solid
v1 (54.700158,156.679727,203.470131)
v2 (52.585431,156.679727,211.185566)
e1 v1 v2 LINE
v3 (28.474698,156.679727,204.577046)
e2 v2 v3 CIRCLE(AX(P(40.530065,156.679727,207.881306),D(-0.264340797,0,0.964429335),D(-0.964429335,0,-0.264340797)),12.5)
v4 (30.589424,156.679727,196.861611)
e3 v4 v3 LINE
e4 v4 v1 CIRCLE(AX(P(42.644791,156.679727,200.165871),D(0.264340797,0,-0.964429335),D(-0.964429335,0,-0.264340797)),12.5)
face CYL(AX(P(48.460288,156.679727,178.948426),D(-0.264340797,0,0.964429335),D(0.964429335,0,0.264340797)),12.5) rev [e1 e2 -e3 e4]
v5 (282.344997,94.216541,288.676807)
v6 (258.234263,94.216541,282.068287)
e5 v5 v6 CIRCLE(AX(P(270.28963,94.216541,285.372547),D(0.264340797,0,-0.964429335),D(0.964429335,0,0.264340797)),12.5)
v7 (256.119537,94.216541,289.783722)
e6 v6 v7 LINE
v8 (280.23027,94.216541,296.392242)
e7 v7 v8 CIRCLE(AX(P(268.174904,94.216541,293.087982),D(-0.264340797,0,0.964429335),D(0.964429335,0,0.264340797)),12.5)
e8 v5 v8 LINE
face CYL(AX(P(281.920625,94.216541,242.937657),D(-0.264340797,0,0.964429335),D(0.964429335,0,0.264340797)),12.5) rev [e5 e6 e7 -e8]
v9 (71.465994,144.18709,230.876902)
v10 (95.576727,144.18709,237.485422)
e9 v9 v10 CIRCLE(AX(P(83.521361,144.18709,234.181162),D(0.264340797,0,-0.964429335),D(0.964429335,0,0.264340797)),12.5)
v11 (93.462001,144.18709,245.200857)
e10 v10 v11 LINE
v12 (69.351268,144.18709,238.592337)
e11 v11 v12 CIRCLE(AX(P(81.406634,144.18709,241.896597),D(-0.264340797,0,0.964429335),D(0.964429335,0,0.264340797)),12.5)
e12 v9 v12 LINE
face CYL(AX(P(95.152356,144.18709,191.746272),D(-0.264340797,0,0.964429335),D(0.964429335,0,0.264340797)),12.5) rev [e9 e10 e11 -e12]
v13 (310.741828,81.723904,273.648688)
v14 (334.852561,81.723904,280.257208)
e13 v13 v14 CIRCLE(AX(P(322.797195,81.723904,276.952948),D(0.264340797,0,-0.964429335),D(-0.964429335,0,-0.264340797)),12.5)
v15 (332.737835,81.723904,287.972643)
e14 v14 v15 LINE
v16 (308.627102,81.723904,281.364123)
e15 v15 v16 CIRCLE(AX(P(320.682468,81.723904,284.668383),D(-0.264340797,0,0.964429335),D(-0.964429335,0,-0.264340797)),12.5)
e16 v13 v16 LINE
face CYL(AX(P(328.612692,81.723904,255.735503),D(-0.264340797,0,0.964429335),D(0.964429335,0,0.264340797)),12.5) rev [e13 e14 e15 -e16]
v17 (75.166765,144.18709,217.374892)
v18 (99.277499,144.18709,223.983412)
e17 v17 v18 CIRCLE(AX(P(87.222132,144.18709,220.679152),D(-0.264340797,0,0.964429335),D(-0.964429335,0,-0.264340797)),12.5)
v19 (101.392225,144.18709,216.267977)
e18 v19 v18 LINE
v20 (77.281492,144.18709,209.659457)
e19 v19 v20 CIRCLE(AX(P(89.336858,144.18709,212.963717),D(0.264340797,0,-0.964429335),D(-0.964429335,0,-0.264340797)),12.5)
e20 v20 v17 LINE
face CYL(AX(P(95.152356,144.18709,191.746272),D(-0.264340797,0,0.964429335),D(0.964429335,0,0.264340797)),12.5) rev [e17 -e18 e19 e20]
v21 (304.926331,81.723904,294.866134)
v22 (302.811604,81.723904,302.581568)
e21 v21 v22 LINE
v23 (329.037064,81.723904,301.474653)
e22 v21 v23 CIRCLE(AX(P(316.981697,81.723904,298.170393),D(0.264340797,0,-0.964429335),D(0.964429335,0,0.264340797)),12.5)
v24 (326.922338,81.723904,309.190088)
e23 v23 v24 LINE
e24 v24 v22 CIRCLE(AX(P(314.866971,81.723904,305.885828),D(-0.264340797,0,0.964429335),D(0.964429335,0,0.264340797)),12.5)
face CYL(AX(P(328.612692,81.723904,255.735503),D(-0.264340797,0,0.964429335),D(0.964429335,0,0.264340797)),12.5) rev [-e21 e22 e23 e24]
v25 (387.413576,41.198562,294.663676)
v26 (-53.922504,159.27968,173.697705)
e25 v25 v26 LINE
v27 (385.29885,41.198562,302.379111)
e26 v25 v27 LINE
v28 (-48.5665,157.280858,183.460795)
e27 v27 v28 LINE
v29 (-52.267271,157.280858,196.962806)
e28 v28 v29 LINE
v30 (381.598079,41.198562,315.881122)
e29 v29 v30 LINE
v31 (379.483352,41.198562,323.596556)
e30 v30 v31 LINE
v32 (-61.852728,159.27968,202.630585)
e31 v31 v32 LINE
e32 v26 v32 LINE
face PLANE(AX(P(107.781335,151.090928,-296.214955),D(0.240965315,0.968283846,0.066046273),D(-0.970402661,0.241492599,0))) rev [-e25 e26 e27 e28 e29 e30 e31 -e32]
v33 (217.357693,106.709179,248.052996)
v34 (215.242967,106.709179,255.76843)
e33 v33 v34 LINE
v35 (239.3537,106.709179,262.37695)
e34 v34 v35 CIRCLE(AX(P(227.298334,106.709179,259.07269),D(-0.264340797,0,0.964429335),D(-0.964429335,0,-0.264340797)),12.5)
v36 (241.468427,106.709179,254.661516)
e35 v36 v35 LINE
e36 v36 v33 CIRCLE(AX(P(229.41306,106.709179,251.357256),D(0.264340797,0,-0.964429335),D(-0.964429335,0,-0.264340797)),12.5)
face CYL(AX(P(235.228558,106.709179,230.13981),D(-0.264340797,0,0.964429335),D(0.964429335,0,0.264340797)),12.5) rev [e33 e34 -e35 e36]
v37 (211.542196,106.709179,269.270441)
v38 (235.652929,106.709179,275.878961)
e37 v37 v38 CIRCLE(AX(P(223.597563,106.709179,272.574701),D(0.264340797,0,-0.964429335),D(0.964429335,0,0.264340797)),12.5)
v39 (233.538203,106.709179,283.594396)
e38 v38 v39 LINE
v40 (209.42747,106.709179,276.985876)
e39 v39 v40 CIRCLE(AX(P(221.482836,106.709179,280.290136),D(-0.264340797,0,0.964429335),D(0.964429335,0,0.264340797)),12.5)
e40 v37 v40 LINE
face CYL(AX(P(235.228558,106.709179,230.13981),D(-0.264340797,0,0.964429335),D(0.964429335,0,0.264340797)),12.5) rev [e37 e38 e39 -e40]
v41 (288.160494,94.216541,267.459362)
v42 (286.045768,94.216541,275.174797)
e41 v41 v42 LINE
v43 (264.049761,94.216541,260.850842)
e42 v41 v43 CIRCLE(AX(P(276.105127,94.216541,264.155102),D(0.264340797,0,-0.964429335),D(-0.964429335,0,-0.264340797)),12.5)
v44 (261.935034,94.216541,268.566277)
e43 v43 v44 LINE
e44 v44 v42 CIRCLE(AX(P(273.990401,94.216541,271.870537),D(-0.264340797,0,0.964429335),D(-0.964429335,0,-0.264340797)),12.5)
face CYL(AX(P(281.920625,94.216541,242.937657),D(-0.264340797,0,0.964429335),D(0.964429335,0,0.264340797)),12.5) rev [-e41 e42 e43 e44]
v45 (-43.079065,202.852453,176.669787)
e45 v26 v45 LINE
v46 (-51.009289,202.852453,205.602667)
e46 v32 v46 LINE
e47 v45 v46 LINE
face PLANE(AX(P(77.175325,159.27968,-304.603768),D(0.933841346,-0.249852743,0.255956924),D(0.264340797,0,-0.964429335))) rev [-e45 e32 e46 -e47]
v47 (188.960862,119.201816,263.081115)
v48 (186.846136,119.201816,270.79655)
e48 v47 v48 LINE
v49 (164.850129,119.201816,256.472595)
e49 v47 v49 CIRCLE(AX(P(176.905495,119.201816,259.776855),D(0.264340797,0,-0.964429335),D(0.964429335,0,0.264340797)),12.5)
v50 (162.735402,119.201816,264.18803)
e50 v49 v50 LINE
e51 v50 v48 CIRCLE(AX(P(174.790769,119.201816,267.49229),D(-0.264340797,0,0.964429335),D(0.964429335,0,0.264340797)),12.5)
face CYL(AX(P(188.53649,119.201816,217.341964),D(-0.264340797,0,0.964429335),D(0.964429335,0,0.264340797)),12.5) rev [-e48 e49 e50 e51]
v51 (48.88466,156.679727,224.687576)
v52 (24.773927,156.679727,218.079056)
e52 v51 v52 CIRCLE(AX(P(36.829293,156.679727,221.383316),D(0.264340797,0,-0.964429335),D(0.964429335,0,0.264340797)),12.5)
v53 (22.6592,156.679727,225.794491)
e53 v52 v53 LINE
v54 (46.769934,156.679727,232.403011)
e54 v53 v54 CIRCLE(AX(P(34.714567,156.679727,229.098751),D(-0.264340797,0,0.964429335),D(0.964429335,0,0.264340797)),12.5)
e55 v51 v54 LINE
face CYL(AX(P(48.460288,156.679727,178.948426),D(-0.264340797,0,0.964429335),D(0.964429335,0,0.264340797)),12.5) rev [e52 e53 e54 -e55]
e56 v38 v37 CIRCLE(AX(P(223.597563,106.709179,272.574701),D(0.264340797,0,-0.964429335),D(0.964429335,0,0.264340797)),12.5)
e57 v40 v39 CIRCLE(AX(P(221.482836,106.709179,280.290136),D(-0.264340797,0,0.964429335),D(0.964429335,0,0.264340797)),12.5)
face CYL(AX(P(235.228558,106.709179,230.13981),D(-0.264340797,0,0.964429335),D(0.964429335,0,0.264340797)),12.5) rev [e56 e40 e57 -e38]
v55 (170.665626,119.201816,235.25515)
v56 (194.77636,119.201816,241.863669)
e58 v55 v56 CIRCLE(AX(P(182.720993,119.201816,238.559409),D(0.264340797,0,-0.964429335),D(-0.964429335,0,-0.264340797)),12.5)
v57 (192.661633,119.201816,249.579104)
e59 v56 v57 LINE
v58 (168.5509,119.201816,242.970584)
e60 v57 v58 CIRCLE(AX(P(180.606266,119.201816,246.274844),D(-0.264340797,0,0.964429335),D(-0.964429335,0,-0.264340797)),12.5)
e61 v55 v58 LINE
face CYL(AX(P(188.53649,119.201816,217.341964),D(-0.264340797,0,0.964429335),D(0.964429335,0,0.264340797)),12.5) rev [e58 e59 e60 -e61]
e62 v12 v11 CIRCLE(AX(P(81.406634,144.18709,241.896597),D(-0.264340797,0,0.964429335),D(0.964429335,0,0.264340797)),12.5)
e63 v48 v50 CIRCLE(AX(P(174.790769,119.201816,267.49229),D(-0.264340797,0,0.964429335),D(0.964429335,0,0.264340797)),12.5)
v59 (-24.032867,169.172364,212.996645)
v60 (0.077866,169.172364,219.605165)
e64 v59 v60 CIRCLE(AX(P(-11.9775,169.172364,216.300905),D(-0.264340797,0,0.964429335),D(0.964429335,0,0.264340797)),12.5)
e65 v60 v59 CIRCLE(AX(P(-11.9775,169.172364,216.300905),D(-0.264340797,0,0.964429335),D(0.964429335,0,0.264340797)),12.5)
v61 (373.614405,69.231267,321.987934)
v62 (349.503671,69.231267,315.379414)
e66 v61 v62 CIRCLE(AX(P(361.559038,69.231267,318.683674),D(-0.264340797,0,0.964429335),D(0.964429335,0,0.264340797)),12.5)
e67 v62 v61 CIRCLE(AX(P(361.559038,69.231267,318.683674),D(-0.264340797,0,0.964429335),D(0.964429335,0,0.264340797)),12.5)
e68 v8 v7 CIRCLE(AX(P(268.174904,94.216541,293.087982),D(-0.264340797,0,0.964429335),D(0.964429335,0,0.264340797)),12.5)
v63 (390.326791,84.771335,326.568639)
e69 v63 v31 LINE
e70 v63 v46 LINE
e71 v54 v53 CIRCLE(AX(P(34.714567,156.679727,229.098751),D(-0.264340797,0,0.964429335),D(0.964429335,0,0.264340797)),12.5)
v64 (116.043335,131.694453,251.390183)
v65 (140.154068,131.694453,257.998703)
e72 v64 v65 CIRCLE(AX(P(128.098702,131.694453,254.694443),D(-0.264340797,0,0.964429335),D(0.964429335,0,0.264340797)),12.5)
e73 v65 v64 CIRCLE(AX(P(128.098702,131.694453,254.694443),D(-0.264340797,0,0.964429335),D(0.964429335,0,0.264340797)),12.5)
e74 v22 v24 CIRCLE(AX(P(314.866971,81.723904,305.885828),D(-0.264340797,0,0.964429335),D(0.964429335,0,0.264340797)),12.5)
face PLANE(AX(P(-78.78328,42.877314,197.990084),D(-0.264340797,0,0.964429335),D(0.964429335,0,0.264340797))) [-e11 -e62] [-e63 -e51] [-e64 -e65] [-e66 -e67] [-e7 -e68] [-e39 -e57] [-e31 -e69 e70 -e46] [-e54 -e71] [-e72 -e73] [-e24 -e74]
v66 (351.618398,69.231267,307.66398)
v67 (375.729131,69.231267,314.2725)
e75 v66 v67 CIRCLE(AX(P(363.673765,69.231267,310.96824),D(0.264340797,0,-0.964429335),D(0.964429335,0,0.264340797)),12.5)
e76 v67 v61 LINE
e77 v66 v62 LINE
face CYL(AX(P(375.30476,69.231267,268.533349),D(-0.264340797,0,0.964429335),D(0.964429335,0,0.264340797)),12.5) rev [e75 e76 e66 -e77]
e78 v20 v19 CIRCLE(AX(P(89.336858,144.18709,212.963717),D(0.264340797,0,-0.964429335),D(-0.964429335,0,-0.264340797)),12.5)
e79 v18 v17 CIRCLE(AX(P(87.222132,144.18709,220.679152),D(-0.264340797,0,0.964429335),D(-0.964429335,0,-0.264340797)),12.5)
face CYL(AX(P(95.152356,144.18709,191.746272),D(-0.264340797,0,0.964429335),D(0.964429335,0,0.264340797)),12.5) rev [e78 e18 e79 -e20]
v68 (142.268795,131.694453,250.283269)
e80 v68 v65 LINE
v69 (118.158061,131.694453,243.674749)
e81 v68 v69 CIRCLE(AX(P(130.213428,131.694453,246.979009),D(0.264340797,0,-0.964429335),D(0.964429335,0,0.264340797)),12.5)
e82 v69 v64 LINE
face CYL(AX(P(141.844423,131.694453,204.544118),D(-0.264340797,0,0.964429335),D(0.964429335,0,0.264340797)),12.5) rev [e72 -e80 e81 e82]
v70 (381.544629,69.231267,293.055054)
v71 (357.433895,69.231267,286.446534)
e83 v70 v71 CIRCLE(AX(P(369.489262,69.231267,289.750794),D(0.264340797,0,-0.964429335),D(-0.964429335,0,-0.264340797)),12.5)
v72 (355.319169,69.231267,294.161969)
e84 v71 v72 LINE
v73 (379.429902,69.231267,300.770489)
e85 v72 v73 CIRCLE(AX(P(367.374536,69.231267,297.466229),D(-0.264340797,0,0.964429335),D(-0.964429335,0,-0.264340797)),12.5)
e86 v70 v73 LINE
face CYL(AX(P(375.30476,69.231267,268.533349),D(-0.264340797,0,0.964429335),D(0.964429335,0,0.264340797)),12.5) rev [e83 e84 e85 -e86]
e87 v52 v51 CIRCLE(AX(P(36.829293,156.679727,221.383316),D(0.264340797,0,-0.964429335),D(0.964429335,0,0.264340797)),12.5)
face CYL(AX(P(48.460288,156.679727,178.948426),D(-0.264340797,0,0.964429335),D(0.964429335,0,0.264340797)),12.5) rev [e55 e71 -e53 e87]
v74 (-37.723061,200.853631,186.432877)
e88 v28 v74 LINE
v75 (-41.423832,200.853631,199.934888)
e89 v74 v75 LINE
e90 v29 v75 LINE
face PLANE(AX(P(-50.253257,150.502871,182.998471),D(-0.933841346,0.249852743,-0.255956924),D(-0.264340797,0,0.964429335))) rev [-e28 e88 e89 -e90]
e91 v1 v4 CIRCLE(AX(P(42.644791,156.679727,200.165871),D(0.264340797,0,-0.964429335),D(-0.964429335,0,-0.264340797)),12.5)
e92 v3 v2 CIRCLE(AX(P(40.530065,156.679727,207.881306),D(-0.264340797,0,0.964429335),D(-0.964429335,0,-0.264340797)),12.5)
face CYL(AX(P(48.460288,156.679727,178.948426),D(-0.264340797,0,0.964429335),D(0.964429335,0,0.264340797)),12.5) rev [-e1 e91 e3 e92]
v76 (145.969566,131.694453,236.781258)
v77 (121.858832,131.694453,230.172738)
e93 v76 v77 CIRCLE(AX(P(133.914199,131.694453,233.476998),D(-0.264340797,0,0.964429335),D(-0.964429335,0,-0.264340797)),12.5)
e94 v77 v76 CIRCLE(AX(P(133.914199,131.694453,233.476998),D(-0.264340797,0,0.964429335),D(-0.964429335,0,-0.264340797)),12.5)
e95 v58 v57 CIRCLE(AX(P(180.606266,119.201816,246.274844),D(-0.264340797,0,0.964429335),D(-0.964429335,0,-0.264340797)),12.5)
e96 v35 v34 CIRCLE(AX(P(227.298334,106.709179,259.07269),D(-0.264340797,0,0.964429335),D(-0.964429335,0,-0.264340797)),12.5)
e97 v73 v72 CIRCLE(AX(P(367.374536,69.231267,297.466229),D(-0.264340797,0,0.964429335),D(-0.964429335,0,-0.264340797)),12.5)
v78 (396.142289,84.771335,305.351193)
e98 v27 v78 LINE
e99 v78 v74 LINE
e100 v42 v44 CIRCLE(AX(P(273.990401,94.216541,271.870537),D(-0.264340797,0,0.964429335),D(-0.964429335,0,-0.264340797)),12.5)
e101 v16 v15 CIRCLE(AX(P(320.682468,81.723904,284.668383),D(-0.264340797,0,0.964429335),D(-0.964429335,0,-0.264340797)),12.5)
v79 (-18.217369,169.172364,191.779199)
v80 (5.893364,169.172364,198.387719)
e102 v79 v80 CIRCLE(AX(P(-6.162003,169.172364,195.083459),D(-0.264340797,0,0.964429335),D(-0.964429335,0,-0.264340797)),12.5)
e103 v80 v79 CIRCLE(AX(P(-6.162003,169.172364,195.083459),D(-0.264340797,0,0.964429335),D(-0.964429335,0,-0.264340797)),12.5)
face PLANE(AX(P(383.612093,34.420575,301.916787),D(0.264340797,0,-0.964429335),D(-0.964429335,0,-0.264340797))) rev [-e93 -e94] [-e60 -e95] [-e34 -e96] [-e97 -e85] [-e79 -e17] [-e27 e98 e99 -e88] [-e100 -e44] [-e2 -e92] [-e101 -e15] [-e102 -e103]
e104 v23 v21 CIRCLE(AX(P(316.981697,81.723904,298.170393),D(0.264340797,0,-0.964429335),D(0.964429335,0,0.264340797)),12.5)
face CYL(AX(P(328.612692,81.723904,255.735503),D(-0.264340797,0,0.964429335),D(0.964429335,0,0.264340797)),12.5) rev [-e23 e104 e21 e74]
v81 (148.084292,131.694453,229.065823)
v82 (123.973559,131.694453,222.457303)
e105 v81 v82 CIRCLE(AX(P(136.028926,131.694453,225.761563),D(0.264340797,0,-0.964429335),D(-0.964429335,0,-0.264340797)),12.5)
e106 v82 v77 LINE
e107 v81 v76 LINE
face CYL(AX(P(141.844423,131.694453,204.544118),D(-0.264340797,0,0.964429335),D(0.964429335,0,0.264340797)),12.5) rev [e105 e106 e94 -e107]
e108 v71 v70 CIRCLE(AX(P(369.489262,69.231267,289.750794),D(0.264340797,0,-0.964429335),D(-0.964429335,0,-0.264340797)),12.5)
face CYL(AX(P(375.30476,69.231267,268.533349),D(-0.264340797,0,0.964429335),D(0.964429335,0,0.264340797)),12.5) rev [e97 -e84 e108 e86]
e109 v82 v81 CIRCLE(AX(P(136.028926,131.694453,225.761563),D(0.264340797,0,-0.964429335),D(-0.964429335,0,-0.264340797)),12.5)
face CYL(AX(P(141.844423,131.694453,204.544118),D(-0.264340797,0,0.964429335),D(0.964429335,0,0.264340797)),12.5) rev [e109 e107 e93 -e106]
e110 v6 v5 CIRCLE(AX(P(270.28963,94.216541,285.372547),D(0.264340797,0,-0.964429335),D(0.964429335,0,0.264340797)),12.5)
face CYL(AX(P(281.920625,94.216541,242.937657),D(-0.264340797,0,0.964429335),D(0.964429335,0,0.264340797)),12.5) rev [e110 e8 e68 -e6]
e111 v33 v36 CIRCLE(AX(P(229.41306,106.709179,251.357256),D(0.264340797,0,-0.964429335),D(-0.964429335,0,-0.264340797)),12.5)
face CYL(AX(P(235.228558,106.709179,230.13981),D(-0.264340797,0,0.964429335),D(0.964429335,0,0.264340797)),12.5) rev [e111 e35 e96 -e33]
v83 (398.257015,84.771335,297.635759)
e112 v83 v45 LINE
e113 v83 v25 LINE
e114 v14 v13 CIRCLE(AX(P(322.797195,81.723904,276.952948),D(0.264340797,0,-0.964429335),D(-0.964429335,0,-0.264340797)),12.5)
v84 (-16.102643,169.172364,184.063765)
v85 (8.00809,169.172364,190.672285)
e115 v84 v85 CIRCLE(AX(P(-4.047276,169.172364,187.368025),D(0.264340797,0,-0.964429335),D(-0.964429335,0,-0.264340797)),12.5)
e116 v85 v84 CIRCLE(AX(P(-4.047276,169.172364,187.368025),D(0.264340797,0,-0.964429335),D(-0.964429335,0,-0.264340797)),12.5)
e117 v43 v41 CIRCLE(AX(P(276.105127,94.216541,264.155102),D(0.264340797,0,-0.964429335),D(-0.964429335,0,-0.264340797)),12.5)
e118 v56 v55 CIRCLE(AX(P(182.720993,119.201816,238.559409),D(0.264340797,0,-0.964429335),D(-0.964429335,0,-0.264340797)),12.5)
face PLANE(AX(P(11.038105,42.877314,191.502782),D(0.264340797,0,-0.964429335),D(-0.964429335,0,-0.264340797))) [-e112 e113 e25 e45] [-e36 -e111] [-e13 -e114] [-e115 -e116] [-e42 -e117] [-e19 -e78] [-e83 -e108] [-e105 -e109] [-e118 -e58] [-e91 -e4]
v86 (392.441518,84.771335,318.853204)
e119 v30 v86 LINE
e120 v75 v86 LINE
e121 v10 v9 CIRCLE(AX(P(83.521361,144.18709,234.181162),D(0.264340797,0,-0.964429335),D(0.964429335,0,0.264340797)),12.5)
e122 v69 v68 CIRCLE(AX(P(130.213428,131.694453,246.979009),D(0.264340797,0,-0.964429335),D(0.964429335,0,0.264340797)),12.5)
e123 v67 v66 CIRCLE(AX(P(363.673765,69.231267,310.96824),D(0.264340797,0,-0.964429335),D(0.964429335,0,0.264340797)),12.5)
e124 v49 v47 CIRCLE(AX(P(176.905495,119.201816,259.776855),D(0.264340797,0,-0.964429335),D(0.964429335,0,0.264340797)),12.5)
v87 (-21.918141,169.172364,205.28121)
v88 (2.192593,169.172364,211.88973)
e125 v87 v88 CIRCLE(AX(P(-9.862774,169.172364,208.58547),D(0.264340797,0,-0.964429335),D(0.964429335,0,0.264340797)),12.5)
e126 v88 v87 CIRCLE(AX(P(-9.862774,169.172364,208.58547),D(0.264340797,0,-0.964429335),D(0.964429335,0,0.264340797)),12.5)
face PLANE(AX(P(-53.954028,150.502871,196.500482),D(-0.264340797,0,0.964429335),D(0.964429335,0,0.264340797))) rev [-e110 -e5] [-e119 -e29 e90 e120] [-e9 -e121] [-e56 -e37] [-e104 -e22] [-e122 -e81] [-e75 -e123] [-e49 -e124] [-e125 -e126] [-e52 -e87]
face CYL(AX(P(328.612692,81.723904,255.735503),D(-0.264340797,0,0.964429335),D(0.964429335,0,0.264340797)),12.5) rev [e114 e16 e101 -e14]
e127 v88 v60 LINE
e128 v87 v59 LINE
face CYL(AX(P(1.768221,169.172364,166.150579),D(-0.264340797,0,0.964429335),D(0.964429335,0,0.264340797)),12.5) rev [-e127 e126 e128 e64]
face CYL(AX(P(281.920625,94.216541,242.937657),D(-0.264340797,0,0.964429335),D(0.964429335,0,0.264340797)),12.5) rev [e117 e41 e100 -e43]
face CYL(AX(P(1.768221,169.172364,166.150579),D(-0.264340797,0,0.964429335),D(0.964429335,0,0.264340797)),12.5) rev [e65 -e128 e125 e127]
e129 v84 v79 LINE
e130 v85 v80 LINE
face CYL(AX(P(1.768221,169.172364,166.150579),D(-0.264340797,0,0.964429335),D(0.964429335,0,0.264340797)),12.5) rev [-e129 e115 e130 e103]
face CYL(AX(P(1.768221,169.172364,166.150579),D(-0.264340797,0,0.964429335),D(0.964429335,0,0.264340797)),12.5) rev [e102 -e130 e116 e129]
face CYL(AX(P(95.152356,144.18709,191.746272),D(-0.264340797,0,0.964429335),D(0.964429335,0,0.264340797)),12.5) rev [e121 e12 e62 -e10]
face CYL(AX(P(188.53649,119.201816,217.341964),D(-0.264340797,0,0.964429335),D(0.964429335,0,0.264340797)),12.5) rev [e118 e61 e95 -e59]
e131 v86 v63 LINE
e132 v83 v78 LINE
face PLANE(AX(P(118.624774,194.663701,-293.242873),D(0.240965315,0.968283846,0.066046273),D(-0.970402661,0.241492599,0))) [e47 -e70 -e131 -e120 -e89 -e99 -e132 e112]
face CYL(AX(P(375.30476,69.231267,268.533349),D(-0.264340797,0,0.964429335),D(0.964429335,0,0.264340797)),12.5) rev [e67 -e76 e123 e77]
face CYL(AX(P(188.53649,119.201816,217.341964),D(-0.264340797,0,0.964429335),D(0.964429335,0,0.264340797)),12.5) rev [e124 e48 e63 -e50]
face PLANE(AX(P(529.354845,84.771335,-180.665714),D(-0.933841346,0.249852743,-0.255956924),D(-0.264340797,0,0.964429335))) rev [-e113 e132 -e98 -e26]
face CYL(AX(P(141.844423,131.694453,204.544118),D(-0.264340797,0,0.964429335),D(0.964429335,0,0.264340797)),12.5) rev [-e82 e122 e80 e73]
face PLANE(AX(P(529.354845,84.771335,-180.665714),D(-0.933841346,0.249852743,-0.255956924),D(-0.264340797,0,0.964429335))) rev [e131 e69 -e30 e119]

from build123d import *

# Parameters (mm, degrees)
EXTRUDE_THIN1_DEPTH      = 15
EXTRUDE_THIN1_DEPTH_BACK = 15
SKETCH2_R                = 12.5
CUT_EXTRUDE1_DEPTH       = 52
CUT_EXTRUDE2_DEPTH       = 52


with BuildPart() as part:
    # Sketch1 → Extrude-Thin1 (new, two sides: drawn at the far end of the back side and taken through both)
    with BuildSketch(Plane(origin=(-52.015152818, 0, 189.77373053), x_dir=(0.9644293353148398, 0, 0.2643407974266862), z_dir=(-0.2643407974266862, 0, 0.9644293353148398)).offset(-EXTRUDE_THIN1_DEPTH_BACK)):
        Polygon((-6.089055059, 159.279680039), (25.645783745, 151.090927797), (451.524648913, 41.198562071), (462.768022338, 84.771335153), (36.889157171, 194.663700878), (5.154318366, 202.85245312), align=None)
    extrude(amount=EXTRUDE_THIN1_DEPTH + EXTRUDE_THIN1_DEPTH_BACK)

    # Sketch2 → Cut-Extrude1 (cut)
    with BuildSketch(Plane(origin=(-55.98026478, 0, 204.240170559), x_dir=(0.9644293353148398, 0, 0.26434079742668615), z_dir=(-0.26434079742668615, 0, 0.9644293353148398))):
        with Locations((432.939239469, 69.231267182)):
            Circle(SKETCH2_R)
        with Locations((384.525047156, 81.723904321)):
            Circle(SKETCH2_R)
        with Locations((336.110854844, 94.216541461)):
            Circle(SKETCH2_R)
        with Locations((287.696662531, 106.7091786)):
            Circle(SKETCH2_R)
        with Locations((239.282470218, 119.20181574)):
            Circle(SKETCH2_R)
        with Locations((190.868277905, 131.694452879)):
            Circle(SKETCH2_R)
        with Locations((142.454085592, 144.187090019)):
            Circle(SKETCH2_R)
        with Locations((94.03989328, 156.679727158)):
            Circle(SKETCH2_R)
        with Locations((45.625700967, 169.172364298)):
            Circle(SKETCH2_R)
    extrude(amount=-CUT_EXTRUDE1_DEPTH, mode=Mode.SUBTRACT)

    # Sketch3 → Cut-Extrude2 (cut)
    with BuildSketch(Plane(origin=(47.64042684, 191.43608201, 13.057782421), x_dir=(0.9705337279727567, -0.24040671124001461, -0.01639805043483442), z_dir=(0.24096531465607895, 0.9682838462558588, 0.06604627326849857))):
        Polygon((359.082690346, -298.87451483), (355.26956046, -312.345225296), (-91.768329186, -185.803010492), (-87.955199299, -172.332300026), align=None)
    extrude(amount=-CUT_EXTRUDE2_DEPTH, mode=Mode.SUBTRACT)


solid = part.part
